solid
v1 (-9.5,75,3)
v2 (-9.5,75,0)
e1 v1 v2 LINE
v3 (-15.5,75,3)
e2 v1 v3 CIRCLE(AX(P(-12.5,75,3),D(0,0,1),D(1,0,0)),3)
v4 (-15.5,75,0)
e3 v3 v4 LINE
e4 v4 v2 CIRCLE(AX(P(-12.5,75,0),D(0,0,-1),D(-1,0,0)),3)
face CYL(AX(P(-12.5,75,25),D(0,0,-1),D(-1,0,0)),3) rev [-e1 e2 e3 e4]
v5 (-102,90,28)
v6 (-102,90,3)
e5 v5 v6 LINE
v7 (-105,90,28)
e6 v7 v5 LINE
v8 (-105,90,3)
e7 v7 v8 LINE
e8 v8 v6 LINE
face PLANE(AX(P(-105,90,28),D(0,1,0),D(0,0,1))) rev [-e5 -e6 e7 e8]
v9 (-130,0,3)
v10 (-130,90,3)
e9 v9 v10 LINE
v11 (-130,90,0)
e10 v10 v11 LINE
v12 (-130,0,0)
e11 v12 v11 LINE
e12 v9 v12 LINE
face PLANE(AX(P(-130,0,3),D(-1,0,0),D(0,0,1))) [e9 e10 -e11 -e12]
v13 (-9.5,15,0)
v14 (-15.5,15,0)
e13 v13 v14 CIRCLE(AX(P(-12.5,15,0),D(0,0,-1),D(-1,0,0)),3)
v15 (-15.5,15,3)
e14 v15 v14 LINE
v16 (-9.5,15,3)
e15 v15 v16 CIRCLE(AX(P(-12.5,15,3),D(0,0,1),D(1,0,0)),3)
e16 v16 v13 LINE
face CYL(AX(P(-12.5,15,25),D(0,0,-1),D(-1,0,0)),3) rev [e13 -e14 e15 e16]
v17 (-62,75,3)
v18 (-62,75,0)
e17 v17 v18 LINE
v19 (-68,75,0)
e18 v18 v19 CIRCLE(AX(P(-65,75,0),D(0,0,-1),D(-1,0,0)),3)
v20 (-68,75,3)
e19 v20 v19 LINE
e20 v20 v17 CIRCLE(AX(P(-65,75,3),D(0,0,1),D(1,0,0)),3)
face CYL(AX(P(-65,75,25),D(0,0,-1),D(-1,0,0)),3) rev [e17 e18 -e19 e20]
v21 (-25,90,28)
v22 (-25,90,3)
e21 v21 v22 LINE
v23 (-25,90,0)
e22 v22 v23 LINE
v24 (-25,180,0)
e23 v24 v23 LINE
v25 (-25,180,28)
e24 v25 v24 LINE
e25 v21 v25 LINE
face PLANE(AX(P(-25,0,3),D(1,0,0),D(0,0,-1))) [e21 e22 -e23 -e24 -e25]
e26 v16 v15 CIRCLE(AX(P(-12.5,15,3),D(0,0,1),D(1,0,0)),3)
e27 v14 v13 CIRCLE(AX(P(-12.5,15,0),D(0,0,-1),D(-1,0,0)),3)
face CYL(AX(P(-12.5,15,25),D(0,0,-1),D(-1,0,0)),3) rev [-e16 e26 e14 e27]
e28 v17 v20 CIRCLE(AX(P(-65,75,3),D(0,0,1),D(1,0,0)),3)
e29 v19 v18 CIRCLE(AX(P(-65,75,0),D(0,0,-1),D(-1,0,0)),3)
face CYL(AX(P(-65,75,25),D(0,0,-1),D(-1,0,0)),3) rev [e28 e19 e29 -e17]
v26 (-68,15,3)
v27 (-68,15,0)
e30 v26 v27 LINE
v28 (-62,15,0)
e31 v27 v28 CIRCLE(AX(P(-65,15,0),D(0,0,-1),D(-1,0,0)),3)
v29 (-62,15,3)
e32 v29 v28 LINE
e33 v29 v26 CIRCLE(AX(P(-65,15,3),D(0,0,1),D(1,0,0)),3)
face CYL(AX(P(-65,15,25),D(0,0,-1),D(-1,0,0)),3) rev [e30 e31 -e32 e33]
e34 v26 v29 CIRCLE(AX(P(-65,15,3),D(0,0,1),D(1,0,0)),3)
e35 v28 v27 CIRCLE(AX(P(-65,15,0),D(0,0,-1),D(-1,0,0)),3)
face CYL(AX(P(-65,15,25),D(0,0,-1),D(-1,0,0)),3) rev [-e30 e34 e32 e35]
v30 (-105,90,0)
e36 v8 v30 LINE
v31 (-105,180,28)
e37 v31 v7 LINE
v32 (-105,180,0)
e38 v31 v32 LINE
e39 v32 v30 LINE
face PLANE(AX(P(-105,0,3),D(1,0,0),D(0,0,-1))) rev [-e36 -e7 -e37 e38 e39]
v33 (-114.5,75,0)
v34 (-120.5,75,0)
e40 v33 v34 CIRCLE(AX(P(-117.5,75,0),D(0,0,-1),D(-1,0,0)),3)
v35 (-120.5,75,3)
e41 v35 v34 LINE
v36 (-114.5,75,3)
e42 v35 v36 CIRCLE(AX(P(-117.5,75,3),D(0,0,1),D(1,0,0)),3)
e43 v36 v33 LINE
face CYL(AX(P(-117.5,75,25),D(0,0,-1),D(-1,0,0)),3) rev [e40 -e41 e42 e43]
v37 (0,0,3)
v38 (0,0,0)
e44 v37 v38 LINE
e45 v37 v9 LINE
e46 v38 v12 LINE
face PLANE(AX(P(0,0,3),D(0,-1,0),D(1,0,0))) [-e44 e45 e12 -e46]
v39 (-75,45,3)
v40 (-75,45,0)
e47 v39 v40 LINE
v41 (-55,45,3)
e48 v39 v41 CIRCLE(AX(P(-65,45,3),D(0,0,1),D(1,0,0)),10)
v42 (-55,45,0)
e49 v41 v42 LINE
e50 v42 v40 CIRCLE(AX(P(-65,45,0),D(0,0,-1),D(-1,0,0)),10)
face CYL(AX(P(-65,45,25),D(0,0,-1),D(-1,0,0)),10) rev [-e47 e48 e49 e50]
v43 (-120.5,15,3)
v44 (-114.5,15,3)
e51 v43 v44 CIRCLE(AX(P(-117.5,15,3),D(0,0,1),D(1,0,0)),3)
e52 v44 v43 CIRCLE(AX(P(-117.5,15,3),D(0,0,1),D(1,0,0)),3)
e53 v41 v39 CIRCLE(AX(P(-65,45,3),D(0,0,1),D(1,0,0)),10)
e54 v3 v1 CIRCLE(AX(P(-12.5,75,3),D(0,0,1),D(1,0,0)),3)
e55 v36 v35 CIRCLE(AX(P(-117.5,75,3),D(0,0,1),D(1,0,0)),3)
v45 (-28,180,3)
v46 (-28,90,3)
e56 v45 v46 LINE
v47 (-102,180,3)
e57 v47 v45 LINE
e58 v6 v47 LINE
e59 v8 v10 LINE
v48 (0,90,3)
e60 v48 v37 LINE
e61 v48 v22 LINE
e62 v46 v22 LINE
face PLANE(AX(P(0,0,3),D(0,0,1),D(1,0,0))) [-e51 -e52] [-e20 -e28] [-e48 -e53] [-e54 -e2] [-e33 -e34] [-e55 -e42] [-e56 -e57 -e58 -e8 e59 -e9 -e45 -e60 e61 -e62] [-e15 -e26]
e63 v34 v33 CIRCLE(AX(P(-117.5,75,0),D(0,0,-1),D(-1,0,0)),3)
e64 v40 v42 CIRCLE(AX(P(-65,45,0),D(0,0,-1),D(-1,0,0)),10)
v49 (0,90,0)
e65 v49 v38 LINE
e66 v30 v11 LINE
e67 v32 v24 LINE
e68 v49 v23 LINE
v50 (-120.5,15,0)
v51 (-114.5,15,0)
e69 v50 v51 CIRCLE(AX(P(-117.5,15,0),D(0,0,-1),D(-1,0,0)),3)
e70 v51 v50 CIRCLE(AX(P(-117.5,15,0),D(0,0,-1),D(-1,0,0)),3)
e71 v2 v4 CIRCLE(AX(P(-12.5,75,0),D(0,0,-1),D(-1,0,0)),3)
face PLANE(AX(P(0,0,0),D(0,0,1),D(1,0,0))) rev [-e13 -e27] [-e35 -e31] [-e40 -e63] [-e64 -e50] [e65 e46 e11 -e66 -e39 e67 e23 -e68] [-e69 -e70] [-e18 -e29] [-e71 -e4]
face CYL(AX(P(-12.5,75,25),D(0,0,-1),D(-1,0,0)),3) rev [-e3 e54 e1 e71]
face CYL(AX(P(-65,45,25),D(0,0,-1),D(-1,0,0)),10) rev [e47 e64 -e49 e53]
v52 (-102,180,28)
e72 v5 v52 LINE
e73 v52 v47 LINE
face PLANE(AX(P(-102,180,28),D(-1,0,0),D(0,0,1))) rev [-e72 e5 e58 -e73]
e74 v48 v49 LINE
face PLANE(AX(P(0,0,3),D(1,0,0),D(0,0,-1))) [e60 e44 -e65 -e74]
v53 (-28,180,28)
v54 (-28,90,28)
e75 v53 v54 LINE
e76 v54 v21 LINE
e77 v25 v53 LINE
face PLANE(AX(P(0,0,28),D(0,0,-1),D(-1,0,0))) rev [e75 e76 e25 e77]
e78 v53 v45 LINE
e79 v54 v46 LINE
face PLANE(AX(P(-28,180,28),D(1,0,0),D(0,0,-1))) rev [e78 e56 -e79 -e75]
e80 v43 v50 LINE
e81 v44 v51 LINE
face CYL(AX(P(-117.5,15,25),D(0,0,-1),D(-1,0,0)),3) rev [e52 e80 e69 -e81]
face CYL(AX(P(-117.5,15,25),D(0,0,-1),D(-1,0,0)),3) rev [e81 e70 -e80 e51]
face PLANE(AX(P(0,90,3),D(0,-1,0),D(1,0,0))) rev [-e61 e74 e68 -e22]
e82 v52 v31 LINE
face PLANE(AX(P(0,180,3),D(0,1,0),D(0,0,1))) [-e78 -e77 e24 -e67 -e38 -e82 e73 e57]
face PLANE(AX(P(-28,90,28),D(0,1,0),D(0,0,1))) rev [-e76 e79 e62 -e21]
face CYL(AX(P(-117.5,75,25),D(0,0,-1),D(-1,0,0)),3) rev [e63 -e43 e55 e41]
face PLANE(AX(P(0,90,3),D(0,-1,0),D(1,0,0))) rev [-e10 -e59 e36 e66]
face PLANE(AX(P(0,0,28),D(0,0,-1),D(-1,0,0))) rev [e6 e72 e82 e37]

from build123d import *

# Parameters (mm, degrees)
SKETCH_1_W          = 80
SKETCH_1_H          = 90
SKETCH_1_W_2        = 130
EXTRUDE_1_DEPTH     = 3
SKETCH_2_W          = 3
SKETCH_2_H          = 90
EXTRUDE_2_DEPTH     = 25
SKETCH_3_R          = 10
SKETCH_3_R_2        = 3
CUT_EXTRUDE_1_DEPTH = 25


with BuildPart() as part:
    # 草图1 → 凸台-拉伸1 (new body)
    with BuildSketch(Plane.XY):
        with Locations((-65, 135)):
            Rectangle(SKETCH_1_W, SKETCH_1_H)
        with Locations((-65, 45)):
            Rectangle(SKETCH_1_W_2, SKETCH_1_H)
    extrude(amount=EXTRUDE_1_DEPTH)

    # 草图2 → 凸台-拉伸2 (add)
    with BuildSketch(Plane.XY.offset(3)):
        with Locations((-103.5, 135)):
            Rectangle(SKETCH_2_W, SKETCH_2_H)
        with Locations((-26.5, 135)):
            Rectangle(SKETCH_2_W, SKETCH_2_H)
    extrude(amount=EXTRUDE_2_DEPTH)

    # 草图3 → 切除-拉伸1 (cut)
    with BuildSketch(Plane(origin=(0, 0, 0), x_dir=(-1, 0, 0), z_dir=(0, 0, -1))):
        with Locations((65, 45)):
            Circle(SKETCH_3_R)
        with Locations((12.5, 15)):
            Circle(SKETCH_3_R_2)
        with Locations((65, 15)):
            Circle(SKETCH_3_R_2)
        with Locations((117.5, 15)):
            Circle(SKETCH_3_R_2)
        with Locations((117.5, 75)):
            Circle(SKETCH_3_R_2)
        with Locations((65, 75)):
            Circle(SKETCH_3_R_2)
        with Locations((12.5, 75)):
            Circle(SKETCH_3_R_2)
    extrude(amount=-CUT_EXTRUDE_1_DEPTH, mode=Mode.SUBTRACT)


solid = part.part
